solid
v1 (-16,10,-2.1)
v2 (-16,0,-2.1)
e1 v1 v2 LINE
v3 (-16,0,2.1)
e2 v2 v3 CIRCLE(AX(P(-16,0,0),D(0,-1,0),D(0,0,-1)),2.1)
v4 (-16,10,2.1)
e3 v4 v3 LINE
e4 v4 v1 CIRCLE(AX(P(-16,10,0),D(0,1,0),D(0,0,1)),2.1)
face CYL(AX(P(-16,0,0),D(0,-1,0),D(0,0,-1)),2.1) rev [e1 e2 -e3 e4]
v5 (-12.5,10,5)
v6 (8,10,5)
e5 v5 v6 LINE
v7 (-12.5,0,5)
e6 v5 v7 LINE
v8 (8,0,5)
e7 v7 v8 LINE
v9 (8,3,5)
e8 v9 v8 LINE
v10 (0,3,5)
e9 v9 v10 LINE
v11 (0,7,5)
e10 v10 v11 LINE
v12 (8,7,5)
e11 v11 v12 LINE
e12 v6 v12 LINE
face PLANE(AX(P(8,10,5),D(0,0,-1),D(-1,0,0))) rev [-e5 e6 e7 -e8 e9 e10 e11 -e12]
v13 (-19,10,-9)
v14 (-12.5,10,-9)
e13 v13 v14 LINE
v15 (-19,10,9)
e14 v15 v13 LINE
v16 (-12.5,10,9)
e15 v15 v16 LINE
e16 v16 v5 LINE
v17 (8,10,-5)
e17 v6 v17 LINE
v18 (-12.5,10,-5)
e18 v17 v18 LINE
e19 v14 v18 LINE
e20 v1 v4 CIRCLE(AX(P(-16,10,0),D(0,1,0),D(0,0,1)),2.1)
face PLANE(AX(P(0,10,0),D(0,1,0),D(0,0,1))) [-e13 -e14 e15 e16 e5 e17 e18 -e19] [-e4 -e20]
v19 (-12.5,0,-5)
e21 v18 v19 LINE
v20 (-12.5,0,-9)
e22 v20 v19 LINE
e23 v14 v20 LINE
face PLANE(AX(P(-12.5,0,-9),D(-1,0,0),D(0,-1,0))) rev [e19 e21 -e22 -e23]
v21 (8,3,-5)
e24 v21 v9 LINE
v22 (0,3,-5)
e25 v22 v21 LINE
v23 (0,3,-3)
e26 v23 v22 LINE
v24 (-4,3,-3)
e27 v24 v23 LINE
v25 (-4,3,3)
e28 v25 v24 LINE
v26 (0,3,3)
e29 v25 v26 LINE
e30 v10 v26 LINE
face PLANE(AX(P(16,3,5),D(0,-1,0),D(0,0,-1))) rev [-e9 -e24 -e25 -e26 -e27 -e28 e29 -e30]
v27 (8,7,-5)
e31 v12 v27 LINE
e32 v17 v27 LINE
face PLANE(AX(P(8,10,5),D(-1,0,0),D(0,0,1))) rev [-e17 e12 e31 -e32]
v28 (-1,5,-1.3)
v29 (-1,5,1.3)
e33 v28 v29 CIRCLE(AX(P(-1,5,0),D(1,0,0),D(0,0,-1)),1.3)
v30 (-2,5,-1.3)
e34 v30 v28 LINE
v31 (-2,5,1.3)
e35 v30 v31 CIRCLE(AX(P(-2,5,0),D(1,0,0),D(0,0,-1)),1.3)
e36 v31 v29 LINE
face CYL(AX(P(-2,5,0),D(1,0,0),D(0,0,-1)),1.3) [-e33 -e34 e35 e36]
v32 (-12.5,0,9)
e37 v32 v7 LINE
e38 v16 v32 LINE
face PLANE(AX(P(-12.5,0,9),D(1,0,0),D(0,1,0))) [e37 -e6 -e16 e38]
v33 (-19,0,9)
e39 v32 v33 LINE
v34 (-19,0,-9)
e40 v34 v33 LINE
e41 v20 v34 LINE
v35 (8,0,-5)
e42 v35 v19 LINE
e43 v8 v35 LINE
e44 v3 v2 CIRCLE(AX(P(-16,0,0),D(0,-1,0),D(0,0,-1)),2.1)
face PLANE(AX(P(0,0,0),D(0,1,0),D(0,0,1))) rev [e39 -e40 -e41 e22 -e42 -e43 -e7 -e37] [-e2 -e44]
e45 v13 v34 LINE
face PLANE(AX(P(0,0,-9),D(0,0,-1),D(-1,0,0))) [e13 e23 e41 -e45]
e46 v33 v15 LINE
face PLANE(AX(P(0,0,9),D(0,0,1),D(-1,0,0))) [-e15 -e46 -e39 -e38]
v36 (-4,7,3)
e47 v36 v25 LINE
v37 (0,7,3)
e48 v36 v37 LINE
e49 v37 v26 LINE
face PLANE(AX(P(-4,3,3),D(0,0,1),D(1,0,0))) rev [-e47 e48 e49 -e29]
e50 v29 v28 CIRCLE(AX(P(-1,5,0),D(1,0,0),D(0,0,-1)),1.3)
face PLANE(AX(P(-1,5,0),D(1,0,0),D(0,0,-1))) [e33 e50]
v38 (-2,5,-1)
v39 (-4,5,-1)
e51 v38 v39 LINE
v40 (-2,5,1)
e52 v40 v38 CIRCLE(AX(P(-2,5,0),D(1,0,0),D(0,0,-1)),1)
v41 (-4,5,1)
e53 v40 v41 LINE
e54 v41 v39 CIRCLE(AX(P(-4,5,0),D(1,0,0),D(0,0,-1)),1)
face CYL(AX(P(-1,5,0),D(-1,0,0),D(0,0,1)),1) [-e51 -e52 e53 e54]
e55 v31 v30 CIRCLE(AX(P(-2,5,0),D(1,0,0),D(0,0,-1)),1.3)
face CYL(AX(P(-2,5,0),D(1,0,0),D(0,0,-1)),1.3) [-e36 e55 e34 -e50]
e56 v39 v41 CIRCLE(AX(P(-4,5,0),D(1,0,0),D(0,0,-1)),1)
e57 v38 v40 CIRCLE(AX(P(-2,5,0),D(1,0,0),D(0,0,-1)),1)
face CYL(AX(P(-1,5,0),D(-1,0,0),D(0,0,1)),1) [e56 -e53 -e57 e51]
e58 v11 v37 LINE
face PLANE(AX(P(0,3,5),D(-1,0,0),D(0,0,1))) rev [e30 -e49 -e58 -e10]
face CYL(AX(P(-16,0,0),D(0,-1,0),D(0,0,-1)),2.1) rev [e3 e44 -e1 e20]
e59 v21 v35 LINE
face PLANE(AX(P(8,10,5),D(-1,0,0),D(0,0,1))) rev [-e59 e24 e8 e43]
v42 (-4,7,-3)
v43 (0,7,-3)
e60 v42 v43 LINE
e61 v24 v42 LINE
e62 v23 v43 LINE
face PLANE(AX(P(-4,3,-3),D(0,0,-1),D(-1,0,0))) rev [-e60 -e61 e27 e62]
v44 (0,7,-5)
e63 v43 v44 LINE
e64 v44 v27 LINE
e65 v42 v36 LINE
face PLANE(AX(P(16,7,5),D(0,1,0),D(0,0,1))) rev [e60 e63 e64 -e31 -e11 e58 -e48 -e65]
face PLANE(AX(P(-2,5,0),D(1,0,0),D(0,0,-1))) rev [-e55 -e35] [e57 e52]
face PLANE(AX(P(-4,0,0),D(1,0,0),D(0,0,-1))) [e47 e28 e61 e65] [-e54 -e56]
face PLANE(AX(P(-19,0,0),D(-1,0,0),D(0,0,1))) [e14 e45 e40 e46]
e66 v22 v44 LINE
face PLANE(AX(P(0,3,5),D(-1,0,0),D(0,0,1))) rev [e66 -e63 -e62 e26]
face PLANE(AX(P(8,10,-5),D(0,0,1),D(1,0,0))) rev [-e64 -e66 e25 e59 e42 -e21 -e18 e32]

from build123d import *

# Parameters (mm, degrees)
SKETCH1_W                   = 16
SKETCH1_H                   = 10
BOSS_EXTRUDE1_DEPTH         = 10
SKETCH2_W                   = 16
SKETCH2_H                   = 4
CUT_EXTRUDE1_DEPTH          = 10
SKETCH3_W                   = 10
SKETCH3_H                   = 10
BOSS_EXTRUDE2_DEPTH         = 7
SKETCH4_W                   = 2.5
SKETCH4_H                   = 10
BOSS_EXTRUDE3_DEPTH         = 4
SKETCH5_W                   = 6
SKETCH5_H                   = 4
CUT_EXTRUDE2_DEPTH          = 4
SKETCH6_R                   = 1
BOSS_EXTRUDE4_DEPTH         = 3
SKETCH7_R                   = 1.3
BOSS_EXTRUDE5_DEPTH         = 1
SKETCH8_W                   = 18
SKETCH8_H                   = 10
BOSS_EXTRUDE6_DEPTH         = 4
TAP_DRILL_FOR_M5_TAP1_D     = 4.2
TAP_DRILL_FOR_M5_TAP1_DEPTH = 60
TAP_DRILL_FOR_M5_TAP1_TIP   = 1.2618073


with BuildPart() as part:
    # Sketch1 → Boss-Extrude1 (new body)
    with BuildSketch(Plane(origin=(0, 0, 0), x_dir=(1, 0, 0), z_dir=(0, 1, 0))):
        Rectangle(SKETCH1_W, SKETCH1_H)
    extrude(amount=BOSS_EXTRUDE1_DEPTH)

    # Sketch2 → Cut-Extrude1 (cut)
    with BuildSketch(Plane(origin=(0, 0, -5), x_dir=(-1, 0, 0), z_dir=(0, 0, -1))):
        with Locations((-8, 5)):
            Rectangle(SKETCH2_W, SKETCH2_H)
    extrude(amount=-CUT_EXTRUDE1_DEPTH, mode=Mode.SUBTRACT)

    # Sketch3 → Boss-Extrude2 (add)
    with BuildSketch(Plane.ZY.offset(8)):
        with Locations((0, 5)):
            Rectangle(SKETCH3_W, SKETCH3_H)
    extrude(amount=BOSS_EXTRUDE2_DEPTH)

    # Sketch4 → Boss-Extrude3 (add)
    with BuildSketch(Plane(origin=(0, 0, -5), x_dir=(-1, 0, 0), z_dir=(0, 0, -1))):
        with Locations((13.75, 5)):
            Rectangle(SKETCH4_W, SKETCH4_H)
    boss_extrude3 = extrude(amount=BOSS_EXTRUDE3_DEPTH)

    # Mirror1: Boss-Extrude3 across plane
    add(boss_extrude3.mirror(Plane(origin=(0, 0, 0), x_dir=(1, 0, 0), z_dir=(0, 0, -1))))

    # Sketch5 → Cut-Extrude2 (cut)
    with BuildSketch(Plane(origin=(0, 0, 0), x_dir=(0, 0, -1), z_dir=(1, 0, 0))):
        with Locations((0, 5)):
            Rectangle(SKETCH5_W, SKETCH5_H)
    extrude(amount=-CUT_EXTRUDE2_DEPTH, mode=Mode.SUBTRACT)

    # Sketch6 → Boss-Extrude4 (add)
    with BuildSketch(Plane(origin=(-4, 0, 0), x_dir=(0, 0, -1), z_dir=(1, 0, 0))):
        with Locations((0, 5)):
            Circle(SKETCH6_R)
    extrude(amount=BOSS_EXTRUDE4_DEPTH)

    # Sketch7 → Boss-Extrude5 (add)
    with BuildSketch(Plane(origin=(-1, 0, 0), x_dir=(0, 0, -1), z_dir=(1, 0, 0))):
        with Locations((0, 5)):
            Circle(SKETCH7_R)
    extrude(amount=-BOSS_EXTRUDE5_DEPTH)

    # Sketch8 → Boss-Extrude6 (add)
    with BuildSketch(Plane.ZY.offset(15)):
        with Locations((0, 5)):
            Rectangle(SKETCH8_W, SKETCH8_H)
    extrude(amount=BOSS_EXTRUDE6_DEPTH)

    # Tap Drill for M5 Tap1
    with Locations(Plane.XZ):
        with Locations((-16, 0)):
            Hole(TAP_DRILL_FOR_M5_TAP1_D / 2, depth=TAP_DRILL_FOR_M5_TAP1_DEPTH)
            with Locations((0, 0, -(TAP_DRILL_FOR_M5_TAP1_DEPTH + TAP_DRILL_FOR_M5_TAP1_TIP / 2))):  # 118° drill point
                Cone(0, TAP_DRILL_FOR_M5_TAP1_D / 2, TAP_DRILL_FOR_M5_TAP1_TIP, mode=Mode.SUBTRACT)


solid = part.part
